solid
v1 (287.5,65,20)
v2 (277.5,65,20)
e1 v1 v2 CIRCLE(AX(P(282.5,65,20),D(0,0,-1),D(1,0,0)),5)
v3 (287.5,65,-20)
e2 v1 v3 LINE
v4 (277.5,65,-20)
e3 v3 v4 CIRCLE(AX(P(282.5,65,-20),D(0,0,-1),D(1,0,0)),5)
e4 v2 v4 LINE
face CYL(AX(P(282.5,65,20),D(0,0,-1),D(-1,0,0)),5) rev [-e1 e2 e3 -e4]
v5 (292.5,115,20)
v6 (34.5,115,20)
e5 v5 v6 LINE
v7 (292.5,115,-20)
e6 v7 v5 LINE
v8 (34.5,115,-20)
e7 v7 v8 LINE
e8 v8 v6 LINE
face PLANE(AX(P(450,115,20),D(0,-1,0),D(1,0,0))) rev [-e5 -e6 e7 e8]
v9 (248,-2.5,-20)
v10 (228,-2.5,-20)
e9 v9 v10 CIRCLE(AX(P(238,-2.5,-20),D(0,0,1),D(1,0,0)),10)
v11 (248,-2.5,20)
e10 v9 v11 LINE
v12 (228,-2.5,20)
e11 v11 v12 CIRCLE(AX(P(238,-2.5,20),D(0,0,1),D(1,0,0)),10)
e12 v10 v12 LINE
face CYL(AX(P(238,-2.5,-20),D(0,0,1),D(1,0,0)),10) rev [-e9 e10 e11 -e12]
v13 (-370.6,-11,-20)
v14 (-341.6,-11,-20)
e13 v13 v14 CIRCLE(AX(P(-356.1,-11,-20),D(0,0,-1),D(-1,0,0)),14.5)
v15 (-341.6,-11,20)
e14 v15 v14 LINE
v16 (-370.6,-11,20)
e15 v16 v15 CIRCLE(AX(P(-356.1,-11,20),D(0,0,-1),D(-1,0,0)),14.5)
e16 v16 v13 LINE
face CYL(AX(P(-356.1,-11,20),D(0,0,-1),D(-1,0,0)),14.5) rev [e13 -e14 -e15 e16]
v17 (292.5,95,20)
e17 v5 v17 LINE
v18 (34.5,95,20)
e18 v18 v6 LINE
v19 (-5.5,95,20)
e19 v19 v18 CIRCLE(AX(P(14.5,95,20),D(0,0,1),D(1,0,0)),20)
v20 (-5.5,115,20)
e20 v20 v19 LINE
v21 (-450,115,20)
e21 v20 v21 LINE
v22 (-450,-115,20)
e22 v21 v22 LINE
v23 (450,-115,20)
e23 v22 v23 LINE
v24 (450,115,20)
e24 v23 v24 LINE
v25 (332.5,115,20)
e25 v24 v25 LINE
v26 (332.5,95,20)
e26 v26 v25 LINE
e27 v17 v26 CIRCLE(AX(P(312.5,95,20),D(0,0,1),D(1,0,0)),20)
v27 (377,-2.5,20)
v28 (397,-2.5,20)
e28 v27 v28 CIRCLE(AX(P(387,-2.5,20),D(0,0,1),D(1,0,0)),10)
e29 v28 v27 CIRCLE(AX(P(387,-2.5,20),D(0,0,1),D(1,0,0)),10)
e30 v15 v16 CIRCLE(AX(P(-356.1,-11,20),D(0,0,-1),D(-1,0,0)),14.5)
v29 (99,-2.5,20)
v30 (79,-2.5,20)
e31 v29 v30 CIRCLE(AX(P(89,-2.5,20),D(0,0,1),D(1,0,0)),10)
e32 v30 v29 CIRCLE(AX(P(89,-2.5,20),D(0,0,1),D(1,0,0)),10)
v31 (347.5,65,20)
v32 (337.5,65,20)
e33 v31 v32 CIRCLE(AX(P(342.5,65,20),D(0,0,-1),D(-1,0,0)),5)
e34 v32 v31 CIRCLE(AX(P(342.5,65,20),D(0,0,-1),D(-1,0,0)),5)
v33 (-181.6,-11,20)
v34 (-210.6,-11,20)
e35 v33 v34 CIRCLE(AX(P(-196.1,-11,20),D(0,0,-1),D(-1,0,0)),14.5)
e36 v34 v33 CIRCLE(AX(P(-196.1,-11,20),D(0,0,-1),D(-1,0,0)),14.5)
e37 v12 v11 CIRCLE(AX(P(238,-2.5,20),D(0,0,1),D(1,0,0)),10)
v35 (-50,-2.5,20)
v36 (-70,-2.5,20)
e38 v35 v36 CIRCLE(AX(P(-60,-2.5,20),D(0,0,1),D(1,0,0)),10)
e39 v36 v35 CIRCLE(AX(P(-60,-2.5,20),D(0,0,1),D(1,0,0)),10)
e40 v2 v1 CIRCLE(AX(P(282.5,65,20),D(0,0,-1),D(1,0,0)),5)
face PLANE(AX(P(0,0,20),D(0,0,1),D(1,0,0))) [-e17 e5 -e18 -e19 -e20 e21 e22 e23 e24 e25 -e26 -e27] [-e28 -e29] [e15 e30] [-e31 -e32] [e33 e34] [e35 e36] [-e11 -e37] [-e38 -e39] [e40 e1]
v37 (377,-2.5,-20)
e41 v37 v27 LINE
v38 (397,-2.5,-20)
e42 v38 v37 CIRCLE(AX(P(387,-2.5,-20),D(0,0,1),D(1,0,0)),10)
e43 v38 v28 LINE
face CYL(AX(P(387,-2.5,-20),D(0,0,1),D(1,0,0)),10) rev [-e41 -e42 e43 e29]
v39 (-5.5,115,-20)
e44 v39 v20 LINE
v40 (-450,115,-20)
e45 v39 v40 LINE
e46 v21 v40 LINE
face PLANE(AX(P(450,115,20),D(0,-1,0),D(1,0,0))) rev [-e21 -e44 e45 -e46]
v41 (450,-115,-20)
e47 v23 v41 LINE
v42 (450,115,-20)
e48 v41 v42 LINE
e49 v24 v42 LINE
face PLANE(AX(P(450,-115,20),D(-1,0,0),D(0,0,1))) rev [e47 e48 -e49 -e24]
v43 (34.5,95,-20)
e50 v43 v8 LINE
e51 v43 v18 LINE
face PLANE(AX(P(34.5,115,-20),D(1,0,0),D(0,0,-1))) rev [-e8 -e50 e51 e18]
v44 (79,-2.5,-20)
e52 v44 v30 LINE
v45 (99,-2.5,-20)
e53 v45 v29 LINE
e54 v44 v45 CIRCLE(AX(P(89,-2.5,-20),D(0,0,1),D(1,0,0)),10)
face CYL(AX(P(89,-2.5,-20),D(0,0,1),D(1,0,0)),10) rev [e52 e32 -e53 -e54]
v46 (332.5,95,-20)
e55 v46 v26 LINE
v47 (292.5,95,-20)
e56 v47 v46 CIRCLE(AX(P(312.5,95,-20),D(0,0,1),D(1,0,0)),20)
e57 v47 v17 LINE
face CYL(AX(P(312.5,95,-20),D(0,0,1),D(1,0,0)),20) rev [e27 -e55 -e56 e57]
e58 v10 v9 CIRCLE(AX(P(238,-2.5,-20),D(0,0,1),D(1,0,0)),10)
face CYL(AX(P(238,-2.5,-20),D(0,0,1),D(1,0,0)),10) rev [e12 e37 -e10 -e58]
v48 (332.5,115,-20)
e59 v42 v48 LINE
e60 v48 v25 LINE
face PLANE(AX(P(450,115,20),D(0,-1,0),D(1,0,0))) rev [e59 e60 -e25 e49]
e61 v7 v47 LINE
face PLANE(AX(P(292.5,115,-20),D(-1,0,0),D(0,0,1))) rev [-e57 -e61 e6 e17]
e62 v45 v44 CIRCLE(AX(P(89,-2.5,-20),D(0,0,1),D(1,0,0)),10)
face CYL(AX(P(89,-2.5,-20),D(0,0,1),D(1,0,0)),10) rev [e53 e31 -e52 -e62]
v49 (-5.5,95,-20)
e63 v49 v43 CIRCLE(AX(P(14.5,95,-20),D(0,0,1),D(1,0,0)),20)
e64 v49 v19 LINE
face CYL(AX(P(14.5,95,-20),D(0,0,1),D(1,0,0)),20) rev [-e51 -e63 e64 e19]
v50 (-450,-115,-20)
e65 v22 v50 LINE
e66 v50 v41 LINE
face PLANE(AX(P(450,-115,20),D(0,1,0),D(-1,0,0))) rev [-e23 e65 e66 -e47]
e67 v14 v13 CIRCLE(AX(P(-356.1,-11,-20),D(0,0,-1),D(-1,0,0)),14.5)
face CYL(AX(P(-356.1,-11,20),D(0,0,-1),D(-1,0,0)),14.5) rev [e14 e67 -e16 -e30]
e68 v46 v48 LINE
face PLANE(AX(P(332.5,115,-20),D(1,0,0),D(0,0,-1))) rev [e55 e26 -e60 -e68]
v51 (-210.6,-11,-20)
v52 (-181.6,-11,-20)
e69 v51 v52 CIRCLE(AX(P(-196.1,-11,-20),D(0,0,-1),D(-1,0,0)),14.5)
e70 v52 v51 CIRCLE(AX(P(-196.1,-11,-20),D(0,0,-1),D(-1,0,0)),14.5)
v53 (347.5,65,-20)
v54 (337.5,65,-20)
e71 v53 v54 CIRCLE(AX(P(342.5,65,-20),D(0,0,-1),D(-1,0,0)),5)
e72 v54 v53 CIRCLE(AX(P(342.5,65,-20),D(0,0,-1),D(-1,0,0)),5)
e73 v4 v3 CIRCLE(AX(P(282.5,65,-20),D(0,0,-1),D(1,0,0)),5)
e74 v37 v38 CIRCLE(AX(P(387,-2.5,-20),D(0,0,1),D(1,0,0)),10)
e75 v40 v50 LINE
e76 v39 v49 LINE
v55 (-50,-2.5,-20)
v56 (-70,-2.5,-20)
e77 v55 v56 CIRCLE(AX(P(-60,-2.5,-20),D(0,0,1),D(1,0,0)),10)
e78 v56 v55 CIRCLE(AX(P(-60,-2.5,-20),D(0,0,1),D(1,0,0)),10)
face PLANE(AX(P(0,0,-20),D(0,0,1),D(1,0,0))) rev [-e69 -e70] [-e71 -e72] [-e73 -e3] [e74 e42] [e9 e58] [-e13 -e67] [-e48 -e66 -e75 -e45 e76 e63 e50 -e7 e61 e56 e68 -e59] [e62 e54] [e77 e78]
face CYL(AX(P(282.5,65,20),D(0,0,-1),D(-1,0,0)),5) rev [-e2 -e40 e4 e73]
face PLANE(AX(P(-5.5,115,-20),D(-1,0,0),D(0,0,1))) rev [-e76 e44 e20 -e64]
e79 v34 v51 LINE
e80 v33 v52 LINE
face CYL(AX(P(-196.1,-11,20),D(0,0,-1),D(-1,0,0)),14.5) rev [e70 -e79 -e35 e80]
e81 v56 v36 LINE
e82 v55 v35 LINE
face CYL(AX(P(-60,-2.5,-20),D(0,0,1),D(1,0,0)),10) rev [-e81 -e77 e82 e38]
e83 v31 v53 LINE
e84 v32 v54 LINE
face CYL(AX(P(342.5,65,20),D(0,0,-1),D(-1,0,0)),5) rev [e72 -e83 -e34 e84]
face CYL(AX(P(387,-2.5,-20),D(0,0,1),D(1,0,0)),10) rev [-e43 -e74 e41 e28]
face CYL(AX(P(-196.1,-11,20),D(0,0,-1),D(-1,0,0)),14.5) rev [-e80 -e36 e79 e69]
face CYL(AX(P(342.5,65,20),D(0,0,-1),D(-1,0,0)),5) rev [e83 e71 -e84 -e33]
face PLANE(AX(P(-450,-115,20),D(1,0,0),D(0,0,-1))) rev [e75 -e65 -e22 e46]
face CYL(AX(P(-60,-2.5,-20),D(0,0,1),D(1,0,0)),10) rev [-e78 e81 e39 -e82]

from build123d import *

# Parameters (mm, degrees)
SKETCH1_W           = 900
SKETCH1_H           = 230
BOSS_EXTRUDE1_DEPTH = 20
SKETCH2_R           = 10
CUT_EXTRUDE1_DEPTH  = 467.181295206
CUT_EXTRUDE2_DEPTH  = 467.181295206
LPATTERN1_COUNT     = 2
LPATTERN1_PITCH     = 298
LPATTERN2_COUNT     = 4
LPATTERN2_PITCH     = 149
SKETCH5_R           = 5
CUT_EXTRUDE4_DEPTH  = 467.181295206
SKETCH6_R           = 14.5
CUT_EXTRUDE5_DEPTH  = 467.181295206


with BuildPart() as part:
    # Sketch1 → Boss-Extrude1 (new, symmetric)
    with BuildSketch(Plane.XY):
        Rectangle(SKETCH1_W, SKETCH1_H)
    extrude(amount=BOSS_EXTRUDE1_DEPTH, both=True)

    # Sketch2 → Cut-Extrude1 (cut, through all)
    with BuildSketch(Plane.XY.offset(20)):
        with Locations((387, -2.5)):
            Circle(SKETCH2_R)
    cut_extrude1 = extrude(amount=-CUT_EXTRUDE1_DEPTH, mode=Mode.SUBTRACT)

    # Sketch3 → Cut-Extrude2 (cut, through all)
    with BuildSketch(Plane.XY.offset(20)):
        with BuildLine():
            Line((332.5, 115), (332.5, 95))
            ThreePointArc((332.5, 95), (312.5, 75), (292.5, 95))
            Line((292.5, 95), (292.5, 115))
            ThreePointArc((292.5, 115), (312.5, 135), (332.5, 115))
        make_face()
    cut_extrude2 = extrude(amount=-CUT_EXTRUDE2_DEPTH, mode=Mode.SUBTRACT)

    # LPattern1: Cut-Extrude2 ×2
    with Locations(*[(-i * LPATTERN1_PITCH, 0, 0) for i in range(1, LPATTERN1_COUNT)]):
        add(cut_extrude2, mode=Mode.SUBTRACT)

    # LPattern2: Cut-Extrude1 ×4
    with Locations(*[(-i * LPATTERN2_PITCH, 0, 0) for i in range(1, LPATTERN2_COUNT)]):
        add(cut_extrude1, mode=Mode.SUBTRACT)

    # Sketch5 → Cut-Extrude4 (cut, through all)
    with BuildSketch(Plane(origin=(0, 0, -20), x_dir=(-1, 0, 0), z_dir=(0, 0, -1))):
        with Locations((-342.5, 65)):
            Circle(SKETCH5_R)
        with Locations(Location((-282.5, 65, 0), (0, 0, 180))):
            Circle(SKETCH5_R)
    extrude(amount=-CUT_EXTRUDE4_DEPTH, mode=Mode.SUBTRACT)

    # Sketch6 → Cut-Extrude5 (cut, through all)
    with BuildSketch(Plane(origin=(0, 0, -20), x_dir=(-1, 0, 0), z_dir=(0, 0, -1))):
        with Locations((356.1, -11)):
            Circle(SKETCH6_R)
        with Locations((196.1, -11)):
            Circle(SKETCH6_R)
    extrude(amount=-CUT_EXTRUDE5_DEPTH, mode=Mode.SUBTRACT)


solid = part.part
